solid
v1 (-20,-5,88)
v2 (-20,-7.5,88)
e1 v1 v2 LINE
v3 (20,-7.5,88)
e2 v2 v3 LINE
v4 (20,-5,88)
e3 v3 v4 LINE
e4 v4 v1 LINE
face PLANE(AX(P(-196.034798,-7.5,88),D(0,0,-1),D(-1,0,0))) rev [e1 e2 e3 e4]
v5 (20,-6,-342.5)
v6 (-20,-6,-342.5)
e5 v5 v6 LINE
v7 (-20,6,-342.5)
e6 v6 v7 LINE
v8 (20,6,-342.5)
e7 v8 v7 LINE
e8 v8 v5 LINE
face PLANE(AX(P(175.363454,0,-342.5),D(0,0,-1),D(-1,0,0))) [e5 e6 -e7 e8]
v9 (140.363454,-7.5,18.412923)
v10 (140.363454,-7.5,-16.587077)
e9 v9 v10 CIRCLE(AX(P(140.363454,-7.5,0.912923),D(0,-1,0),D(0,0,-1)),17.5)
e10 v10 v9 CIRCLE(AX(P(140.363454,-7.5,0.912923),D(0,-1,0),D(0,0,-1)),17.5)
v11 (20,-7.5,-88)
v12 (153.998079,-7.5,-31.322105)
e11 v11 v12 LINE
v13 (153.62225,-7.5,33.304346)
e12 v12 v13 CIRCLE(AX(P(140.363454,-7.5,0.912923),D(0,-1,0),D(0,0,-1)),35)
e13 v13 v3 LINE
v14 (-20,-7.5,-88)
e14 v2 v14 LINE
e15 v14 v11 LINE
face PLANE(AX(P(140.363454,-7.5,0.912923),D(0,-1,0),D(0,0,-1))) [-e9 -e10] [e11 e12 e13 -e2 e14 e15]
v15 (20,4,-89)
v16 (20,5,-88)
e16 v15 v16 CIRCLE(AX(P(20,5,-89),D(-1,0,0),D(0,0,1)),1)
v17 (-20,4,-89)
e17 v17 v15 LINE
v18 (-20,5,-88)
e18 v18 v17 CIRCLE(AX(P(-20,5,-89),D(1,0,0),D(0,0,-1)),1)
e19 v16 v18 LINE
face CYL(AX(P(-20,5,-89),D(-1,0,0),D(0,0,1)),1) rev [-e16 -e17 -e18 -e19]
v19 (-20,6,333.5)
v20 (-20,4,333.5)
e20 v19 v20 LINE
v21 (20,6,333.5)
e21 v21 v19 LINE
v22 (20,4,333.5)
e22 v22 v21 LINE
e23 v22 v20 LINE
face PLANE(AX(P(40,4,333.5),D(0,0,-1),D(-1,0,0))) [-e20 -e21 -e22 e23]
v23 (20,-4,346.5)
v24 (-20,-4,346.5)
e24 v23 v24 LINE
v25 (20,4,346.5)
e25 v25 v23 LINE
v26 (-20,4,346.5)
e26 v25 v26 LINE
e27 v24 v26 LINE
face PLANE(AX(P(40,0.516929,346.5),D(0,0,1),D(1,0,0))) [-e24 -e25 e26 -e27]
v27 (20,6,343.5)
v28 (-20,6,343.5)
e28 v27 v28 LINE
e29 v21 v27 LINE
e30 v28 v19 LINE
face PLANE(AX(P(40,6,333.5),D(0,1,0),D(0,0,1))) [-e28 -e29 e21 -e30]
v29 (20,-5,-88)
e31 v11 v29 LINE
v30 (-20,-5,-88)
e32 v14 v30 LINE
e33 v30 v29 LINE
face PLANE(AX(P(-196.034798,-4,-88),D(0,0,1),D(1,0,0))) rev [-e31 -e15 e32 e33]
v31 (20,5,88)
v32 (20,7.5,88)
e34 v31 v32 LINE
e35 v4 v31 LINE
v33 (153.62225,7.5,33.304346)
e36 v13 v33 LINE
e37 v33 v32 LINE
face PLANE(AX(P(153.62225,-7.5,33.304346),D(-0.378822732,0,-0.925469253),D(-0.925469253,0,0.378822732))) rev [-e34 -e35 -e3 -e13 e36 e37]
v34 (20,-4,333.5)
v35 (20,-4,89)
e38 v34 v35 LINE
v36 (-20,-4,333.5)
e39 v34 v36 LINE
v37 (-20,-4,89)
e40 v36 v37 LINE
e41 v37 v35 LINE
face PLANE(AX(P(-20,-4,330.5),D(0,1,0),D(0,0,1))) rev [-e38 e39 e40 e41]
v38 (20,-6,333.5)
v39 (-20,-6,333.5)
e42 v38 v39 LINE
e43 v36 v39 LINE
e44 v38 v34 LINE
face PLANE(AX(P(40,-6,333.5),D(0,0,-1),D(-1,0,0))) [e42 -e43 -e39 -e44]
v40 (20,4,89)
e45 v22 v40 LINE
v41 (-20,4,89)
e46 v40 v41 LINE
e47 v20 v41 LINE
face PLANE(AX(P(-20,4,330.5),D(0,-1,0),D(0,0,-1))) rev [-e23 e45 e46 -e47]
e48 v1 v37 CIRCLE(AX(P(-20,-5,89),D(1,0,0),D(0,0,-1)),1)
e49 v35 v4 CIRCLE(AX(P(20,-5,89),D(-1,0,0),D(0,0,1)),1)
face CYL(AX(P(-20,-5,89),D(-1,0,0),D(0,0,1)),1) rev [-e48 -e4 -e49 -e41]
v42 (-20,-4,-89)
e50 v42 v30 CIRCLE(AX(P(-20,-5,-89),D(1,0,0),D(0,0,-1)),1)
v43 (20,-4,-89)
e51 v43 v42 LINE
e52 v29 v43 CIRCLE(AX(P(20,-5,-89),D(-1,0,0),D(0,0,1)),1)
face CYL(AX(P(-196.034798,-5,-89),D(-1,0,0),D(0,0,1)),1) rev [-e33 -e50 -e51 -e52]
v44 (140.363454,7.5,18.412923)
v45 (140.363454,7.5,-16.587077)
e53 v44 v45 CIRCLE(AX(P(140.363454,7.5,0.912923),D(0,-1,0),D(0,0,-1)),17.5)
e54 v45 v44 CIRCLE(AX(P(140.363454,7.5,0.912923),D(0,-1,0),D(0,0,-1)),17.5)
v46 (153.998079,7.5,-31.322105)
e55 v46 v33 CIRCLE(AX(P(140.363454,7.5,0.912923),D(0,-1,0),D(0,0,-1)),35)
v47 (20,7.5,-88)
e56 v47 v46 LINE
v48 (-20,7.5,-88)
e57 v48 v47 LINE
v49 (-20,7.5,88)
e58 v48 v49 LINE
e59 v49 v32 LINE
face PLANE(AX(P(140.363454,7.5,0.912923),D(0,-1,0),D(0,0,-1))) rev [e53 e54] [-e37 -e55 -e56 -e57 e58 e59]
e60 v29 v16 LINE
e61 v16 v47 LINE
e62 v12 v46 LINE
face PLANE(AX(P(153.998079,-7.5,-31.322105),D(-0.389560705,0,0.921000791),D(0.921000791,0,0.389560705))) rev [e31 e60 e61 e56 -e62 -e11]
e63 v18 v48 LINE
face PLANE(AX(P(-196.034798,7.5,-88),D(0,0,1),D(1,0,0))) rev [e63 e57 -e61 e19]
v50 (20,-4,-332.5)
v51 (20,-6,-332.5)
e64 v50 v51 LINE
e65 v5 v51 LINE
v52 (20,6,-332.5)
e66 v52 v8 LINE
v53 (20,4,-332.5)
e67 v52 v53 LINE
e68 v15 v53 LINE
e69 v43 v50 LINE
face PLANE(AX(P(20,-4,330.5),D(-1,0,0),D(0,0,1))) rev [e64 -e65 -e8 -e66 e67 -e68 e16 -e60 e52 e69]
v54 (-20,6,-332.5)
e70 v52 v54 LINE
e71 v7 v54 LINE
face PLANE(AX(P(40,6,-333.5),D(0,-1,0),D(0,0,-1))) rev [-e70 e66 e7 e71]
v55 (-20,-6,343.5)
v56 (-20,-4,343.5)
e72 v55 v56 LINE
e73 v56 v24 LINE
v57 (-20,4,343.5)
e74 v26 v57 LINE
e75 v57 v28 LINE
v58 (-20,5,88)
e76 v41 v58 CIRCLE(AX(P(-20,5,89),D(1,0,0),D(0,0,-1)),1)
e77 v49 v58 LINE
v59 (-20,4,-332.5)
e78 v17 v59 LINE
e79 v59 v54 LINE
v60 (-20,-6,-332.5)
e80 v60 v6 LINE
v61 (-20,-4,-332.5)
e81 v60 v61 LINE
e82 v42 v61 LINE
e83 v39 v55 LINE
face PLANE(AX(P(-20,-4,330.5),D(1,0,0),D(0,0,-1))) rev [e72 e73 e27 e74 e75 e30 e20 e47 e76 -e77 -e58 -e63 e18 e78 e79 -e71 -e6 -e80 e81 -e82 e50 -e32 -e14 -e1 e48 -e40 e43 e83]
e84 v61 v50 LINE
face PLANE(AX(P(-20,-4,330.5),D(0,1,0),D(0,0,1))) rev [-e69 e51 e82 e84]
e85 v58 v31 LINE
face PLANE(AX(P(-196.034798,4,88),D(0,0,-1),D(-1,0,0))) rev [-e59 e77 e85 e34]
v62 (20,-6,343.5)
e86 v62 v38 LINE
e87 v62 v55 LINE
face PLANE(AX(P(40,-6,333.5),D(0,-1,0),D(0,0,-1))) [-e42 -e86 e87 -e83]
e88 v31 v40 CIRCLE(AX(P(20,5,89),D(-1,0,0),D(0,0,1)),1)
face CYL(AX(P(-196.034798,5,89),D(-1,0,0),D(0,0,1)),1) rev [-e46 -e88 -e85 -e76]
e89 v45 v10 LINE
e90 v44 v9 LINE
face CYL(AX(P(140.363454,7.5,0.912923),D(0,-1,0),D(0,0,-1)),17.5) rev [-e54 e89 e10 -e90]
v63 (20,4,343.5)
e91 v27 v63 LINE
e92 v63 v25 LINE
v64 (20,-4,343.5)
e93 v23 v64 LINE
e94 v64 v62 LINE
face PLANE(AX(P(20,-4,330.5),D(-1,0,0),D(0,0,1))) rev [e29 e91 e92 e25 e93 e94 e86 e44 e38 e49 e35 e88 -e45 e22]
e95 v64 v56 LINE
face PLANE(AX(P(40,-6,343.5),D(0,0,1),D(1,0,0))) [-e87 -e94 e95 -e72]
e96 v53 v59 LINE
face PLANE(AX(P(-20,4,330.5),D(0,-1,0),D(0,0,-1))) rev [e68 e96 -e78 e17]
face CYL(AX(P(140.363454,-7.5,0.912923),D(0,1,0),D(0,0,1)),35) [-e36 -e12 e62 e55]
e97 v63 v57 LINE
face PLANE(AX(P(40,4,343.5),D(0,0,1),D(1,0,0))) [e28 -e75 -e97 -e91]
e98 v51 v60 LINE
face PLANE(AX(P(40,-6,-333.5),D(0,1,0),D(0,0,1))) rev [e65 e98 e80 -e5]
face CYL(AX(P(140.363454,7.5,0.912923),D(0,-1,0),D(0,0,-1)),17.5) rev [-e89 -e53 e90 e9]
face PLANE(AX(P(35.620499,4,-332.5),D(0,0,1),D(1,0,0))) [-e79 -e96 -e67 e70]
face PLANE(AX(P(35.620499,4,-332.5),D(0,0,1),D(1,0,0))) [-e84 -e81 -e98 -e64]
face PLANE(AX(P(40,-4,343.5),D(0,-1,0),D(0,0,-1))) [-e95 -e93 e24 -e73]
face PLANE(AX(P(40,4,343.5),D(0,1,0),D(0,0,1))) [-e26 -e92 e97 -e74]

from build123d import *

# Parameters (mm, degrees)
SKETCH_1_W               = 40
SKETCH_1_H               = 8
EXTRUDE_1_DEPTH          = 330.5
EXTRUDE_START            = -4
EXTRUDE_9_DEPTH          = 7.5
CUT_EXTRUDE_1_DEPTH      = 375.443041078
CUT_EXTRUDE_1_DEPTH_BACK = 375.443041078
SKETCH_14_R              = 17.5
EXTRUDE_10_DEPTH         = 40
SKETCH_16_W              = 176
SKETCH_16_H              = 3.5
EXTRUDE_11_DEPTH         = 40
SKETCH_17_W              = 176
SKETCH_17_H              = 3.5
EXTRUDE_12_DEPTH         = 40
FILLET_1_R               = 1
CUT_EXTRUDE_2_DEPTH      = 398.850950952
CUT_EXTRUDE_2_DEPTH_BACK = 398.850950952
EXTRUDE_13_DEPTH         = 40


with BuildPart() as part:
    # 草图1 → 凸台-拉伸1 (new, symmetric)
    with BuildSketch(Plane.XY):
        Rectangle(SKETCH_1_W, SKETCH_1_H)
    extrude(amount=EXTRUDE_1_DEPTH, both=True)

    # 草图13 → 凸台-拉伸9 (add, symmetric)
    with BuildSketch(Plane.XZ.offset(4).offset(EXTRUDE_START)):
        with BuildLine():
            Line((153.622249649, 33.30434644), (20, 88))
            Line((20, 88), (20, -88))
            Line((20, -88), (153.998078719, -31.322105093))
            ThreePointArc((153.998078719, -31.322105093), (175.362862221, 1.116458369), (153.622249649, 33.30434644))
        make_face()
    extrude(amount=EXTRUDE_9_DEPTH, both=True)

    # 草图14 → 切除-拉伸1 (cut, two sides: drawn at the far end of the back side and taken through both)
    with BuildSketch(Plane.XZ.offset(7.5).offset(-CUT_EXTRUDE_1_DEPTH_BACK)):
        with Locations(Location((140.363454038, 0.912922591, 0), (0, 0, 270))):
            Circle(SKETCH_14_R)
    extrude(amount=CUT_EXTRUDE_1_DEPTH + CUT_EXTRUDE_1_DEPTH_BACK, mode=Mode.SUBTRACT)

    # 草图15 → 凸台-拉伸10 (add)
    with BuildSketch(Plane.ZY.offset(20)):
        Polygon((330.5, 4), (333.5, 4), (333.5, 6), (343.5, 6), (343.5, 4), (346.5, 4), (346.5, 0.516928803), (346.5, -4), (343.5, -4), (343.5, -6), (333.5, -6), (333.5, -4), (330.5, -4), align=None)
    extrude_10 = extrude(amount=-EXTRUDE_10_DEPTH)

    # 草图16 → 凸台-拉伸11 (add)
    with BuildSketch(Plane.ZY.offset(-20)):
        with Locations((0, 5.75)):
            Rectangle(SKETCH_16_W, SKETCH_16_H)
    extrude(amount=EXTRUDE_11_DEPTH)

    # 草图17 → 凸台-拉伸12 (add)
    with BuildSketch(Plane.ZY.offset(-20)):
        with Locations((0, -5.75)):
            Rectangle(SKETCH_17_W, SKETCH_17_H)
    extrude(amount=EXTRUDE_12_DEPTH)

    # 镜向1: 凸台-拉伸10 across plane
    add(extrude_10.mirror(Plane.XY))

    # 圆角1
    fillet_1_edges = [part.edges().sort_by_distance(p)[0] for p in [
        (0, 4, 88),
        (0, 4, -88),
        (0, -4, -88),
        (0, -4, 88),
    ]]
    fillet(fillet_1_edges, radius=FILLET_1_R)

    # 草图18 → 切除-拉伸2 (cut, two sides: drawn at the far end of the back side and taken through both)
    with BuildSketch(Plane.ZY.offset(20).offset(-CUT_EXTRUDE_2_DEPTH_BACK)):
        Polygon((-339.5, 4), (-339.5, 6), (-343.5, 6), (-343.5, 4), (-346.5, 4), (-346.5, -4), (-343.5, -4), (-343.5, -6), (-339.5, -6), (-339.5, -4), (-342.5, -4), (-342.5, 4), align=None)
    extrude(amount=CUT_EXTRUDE_2_DEPTH + CUT_EXTRUDE_2_DEPTH_BACK, mode=Mode.SUBTRACT)

    # 草图19 → 凸台-拉伸13 (add)
    with BuildSketch(Plane.ZY.offset(20)):
        Polygon((-332.5, 4), (-332.5, 6), (-342.5, 6), (-342.5, -6), (-332.5, -6), (-332.5, -4), align=None)
    extrude(amount=-EXTRUDE_13_DEPTH)


solid = part.part
